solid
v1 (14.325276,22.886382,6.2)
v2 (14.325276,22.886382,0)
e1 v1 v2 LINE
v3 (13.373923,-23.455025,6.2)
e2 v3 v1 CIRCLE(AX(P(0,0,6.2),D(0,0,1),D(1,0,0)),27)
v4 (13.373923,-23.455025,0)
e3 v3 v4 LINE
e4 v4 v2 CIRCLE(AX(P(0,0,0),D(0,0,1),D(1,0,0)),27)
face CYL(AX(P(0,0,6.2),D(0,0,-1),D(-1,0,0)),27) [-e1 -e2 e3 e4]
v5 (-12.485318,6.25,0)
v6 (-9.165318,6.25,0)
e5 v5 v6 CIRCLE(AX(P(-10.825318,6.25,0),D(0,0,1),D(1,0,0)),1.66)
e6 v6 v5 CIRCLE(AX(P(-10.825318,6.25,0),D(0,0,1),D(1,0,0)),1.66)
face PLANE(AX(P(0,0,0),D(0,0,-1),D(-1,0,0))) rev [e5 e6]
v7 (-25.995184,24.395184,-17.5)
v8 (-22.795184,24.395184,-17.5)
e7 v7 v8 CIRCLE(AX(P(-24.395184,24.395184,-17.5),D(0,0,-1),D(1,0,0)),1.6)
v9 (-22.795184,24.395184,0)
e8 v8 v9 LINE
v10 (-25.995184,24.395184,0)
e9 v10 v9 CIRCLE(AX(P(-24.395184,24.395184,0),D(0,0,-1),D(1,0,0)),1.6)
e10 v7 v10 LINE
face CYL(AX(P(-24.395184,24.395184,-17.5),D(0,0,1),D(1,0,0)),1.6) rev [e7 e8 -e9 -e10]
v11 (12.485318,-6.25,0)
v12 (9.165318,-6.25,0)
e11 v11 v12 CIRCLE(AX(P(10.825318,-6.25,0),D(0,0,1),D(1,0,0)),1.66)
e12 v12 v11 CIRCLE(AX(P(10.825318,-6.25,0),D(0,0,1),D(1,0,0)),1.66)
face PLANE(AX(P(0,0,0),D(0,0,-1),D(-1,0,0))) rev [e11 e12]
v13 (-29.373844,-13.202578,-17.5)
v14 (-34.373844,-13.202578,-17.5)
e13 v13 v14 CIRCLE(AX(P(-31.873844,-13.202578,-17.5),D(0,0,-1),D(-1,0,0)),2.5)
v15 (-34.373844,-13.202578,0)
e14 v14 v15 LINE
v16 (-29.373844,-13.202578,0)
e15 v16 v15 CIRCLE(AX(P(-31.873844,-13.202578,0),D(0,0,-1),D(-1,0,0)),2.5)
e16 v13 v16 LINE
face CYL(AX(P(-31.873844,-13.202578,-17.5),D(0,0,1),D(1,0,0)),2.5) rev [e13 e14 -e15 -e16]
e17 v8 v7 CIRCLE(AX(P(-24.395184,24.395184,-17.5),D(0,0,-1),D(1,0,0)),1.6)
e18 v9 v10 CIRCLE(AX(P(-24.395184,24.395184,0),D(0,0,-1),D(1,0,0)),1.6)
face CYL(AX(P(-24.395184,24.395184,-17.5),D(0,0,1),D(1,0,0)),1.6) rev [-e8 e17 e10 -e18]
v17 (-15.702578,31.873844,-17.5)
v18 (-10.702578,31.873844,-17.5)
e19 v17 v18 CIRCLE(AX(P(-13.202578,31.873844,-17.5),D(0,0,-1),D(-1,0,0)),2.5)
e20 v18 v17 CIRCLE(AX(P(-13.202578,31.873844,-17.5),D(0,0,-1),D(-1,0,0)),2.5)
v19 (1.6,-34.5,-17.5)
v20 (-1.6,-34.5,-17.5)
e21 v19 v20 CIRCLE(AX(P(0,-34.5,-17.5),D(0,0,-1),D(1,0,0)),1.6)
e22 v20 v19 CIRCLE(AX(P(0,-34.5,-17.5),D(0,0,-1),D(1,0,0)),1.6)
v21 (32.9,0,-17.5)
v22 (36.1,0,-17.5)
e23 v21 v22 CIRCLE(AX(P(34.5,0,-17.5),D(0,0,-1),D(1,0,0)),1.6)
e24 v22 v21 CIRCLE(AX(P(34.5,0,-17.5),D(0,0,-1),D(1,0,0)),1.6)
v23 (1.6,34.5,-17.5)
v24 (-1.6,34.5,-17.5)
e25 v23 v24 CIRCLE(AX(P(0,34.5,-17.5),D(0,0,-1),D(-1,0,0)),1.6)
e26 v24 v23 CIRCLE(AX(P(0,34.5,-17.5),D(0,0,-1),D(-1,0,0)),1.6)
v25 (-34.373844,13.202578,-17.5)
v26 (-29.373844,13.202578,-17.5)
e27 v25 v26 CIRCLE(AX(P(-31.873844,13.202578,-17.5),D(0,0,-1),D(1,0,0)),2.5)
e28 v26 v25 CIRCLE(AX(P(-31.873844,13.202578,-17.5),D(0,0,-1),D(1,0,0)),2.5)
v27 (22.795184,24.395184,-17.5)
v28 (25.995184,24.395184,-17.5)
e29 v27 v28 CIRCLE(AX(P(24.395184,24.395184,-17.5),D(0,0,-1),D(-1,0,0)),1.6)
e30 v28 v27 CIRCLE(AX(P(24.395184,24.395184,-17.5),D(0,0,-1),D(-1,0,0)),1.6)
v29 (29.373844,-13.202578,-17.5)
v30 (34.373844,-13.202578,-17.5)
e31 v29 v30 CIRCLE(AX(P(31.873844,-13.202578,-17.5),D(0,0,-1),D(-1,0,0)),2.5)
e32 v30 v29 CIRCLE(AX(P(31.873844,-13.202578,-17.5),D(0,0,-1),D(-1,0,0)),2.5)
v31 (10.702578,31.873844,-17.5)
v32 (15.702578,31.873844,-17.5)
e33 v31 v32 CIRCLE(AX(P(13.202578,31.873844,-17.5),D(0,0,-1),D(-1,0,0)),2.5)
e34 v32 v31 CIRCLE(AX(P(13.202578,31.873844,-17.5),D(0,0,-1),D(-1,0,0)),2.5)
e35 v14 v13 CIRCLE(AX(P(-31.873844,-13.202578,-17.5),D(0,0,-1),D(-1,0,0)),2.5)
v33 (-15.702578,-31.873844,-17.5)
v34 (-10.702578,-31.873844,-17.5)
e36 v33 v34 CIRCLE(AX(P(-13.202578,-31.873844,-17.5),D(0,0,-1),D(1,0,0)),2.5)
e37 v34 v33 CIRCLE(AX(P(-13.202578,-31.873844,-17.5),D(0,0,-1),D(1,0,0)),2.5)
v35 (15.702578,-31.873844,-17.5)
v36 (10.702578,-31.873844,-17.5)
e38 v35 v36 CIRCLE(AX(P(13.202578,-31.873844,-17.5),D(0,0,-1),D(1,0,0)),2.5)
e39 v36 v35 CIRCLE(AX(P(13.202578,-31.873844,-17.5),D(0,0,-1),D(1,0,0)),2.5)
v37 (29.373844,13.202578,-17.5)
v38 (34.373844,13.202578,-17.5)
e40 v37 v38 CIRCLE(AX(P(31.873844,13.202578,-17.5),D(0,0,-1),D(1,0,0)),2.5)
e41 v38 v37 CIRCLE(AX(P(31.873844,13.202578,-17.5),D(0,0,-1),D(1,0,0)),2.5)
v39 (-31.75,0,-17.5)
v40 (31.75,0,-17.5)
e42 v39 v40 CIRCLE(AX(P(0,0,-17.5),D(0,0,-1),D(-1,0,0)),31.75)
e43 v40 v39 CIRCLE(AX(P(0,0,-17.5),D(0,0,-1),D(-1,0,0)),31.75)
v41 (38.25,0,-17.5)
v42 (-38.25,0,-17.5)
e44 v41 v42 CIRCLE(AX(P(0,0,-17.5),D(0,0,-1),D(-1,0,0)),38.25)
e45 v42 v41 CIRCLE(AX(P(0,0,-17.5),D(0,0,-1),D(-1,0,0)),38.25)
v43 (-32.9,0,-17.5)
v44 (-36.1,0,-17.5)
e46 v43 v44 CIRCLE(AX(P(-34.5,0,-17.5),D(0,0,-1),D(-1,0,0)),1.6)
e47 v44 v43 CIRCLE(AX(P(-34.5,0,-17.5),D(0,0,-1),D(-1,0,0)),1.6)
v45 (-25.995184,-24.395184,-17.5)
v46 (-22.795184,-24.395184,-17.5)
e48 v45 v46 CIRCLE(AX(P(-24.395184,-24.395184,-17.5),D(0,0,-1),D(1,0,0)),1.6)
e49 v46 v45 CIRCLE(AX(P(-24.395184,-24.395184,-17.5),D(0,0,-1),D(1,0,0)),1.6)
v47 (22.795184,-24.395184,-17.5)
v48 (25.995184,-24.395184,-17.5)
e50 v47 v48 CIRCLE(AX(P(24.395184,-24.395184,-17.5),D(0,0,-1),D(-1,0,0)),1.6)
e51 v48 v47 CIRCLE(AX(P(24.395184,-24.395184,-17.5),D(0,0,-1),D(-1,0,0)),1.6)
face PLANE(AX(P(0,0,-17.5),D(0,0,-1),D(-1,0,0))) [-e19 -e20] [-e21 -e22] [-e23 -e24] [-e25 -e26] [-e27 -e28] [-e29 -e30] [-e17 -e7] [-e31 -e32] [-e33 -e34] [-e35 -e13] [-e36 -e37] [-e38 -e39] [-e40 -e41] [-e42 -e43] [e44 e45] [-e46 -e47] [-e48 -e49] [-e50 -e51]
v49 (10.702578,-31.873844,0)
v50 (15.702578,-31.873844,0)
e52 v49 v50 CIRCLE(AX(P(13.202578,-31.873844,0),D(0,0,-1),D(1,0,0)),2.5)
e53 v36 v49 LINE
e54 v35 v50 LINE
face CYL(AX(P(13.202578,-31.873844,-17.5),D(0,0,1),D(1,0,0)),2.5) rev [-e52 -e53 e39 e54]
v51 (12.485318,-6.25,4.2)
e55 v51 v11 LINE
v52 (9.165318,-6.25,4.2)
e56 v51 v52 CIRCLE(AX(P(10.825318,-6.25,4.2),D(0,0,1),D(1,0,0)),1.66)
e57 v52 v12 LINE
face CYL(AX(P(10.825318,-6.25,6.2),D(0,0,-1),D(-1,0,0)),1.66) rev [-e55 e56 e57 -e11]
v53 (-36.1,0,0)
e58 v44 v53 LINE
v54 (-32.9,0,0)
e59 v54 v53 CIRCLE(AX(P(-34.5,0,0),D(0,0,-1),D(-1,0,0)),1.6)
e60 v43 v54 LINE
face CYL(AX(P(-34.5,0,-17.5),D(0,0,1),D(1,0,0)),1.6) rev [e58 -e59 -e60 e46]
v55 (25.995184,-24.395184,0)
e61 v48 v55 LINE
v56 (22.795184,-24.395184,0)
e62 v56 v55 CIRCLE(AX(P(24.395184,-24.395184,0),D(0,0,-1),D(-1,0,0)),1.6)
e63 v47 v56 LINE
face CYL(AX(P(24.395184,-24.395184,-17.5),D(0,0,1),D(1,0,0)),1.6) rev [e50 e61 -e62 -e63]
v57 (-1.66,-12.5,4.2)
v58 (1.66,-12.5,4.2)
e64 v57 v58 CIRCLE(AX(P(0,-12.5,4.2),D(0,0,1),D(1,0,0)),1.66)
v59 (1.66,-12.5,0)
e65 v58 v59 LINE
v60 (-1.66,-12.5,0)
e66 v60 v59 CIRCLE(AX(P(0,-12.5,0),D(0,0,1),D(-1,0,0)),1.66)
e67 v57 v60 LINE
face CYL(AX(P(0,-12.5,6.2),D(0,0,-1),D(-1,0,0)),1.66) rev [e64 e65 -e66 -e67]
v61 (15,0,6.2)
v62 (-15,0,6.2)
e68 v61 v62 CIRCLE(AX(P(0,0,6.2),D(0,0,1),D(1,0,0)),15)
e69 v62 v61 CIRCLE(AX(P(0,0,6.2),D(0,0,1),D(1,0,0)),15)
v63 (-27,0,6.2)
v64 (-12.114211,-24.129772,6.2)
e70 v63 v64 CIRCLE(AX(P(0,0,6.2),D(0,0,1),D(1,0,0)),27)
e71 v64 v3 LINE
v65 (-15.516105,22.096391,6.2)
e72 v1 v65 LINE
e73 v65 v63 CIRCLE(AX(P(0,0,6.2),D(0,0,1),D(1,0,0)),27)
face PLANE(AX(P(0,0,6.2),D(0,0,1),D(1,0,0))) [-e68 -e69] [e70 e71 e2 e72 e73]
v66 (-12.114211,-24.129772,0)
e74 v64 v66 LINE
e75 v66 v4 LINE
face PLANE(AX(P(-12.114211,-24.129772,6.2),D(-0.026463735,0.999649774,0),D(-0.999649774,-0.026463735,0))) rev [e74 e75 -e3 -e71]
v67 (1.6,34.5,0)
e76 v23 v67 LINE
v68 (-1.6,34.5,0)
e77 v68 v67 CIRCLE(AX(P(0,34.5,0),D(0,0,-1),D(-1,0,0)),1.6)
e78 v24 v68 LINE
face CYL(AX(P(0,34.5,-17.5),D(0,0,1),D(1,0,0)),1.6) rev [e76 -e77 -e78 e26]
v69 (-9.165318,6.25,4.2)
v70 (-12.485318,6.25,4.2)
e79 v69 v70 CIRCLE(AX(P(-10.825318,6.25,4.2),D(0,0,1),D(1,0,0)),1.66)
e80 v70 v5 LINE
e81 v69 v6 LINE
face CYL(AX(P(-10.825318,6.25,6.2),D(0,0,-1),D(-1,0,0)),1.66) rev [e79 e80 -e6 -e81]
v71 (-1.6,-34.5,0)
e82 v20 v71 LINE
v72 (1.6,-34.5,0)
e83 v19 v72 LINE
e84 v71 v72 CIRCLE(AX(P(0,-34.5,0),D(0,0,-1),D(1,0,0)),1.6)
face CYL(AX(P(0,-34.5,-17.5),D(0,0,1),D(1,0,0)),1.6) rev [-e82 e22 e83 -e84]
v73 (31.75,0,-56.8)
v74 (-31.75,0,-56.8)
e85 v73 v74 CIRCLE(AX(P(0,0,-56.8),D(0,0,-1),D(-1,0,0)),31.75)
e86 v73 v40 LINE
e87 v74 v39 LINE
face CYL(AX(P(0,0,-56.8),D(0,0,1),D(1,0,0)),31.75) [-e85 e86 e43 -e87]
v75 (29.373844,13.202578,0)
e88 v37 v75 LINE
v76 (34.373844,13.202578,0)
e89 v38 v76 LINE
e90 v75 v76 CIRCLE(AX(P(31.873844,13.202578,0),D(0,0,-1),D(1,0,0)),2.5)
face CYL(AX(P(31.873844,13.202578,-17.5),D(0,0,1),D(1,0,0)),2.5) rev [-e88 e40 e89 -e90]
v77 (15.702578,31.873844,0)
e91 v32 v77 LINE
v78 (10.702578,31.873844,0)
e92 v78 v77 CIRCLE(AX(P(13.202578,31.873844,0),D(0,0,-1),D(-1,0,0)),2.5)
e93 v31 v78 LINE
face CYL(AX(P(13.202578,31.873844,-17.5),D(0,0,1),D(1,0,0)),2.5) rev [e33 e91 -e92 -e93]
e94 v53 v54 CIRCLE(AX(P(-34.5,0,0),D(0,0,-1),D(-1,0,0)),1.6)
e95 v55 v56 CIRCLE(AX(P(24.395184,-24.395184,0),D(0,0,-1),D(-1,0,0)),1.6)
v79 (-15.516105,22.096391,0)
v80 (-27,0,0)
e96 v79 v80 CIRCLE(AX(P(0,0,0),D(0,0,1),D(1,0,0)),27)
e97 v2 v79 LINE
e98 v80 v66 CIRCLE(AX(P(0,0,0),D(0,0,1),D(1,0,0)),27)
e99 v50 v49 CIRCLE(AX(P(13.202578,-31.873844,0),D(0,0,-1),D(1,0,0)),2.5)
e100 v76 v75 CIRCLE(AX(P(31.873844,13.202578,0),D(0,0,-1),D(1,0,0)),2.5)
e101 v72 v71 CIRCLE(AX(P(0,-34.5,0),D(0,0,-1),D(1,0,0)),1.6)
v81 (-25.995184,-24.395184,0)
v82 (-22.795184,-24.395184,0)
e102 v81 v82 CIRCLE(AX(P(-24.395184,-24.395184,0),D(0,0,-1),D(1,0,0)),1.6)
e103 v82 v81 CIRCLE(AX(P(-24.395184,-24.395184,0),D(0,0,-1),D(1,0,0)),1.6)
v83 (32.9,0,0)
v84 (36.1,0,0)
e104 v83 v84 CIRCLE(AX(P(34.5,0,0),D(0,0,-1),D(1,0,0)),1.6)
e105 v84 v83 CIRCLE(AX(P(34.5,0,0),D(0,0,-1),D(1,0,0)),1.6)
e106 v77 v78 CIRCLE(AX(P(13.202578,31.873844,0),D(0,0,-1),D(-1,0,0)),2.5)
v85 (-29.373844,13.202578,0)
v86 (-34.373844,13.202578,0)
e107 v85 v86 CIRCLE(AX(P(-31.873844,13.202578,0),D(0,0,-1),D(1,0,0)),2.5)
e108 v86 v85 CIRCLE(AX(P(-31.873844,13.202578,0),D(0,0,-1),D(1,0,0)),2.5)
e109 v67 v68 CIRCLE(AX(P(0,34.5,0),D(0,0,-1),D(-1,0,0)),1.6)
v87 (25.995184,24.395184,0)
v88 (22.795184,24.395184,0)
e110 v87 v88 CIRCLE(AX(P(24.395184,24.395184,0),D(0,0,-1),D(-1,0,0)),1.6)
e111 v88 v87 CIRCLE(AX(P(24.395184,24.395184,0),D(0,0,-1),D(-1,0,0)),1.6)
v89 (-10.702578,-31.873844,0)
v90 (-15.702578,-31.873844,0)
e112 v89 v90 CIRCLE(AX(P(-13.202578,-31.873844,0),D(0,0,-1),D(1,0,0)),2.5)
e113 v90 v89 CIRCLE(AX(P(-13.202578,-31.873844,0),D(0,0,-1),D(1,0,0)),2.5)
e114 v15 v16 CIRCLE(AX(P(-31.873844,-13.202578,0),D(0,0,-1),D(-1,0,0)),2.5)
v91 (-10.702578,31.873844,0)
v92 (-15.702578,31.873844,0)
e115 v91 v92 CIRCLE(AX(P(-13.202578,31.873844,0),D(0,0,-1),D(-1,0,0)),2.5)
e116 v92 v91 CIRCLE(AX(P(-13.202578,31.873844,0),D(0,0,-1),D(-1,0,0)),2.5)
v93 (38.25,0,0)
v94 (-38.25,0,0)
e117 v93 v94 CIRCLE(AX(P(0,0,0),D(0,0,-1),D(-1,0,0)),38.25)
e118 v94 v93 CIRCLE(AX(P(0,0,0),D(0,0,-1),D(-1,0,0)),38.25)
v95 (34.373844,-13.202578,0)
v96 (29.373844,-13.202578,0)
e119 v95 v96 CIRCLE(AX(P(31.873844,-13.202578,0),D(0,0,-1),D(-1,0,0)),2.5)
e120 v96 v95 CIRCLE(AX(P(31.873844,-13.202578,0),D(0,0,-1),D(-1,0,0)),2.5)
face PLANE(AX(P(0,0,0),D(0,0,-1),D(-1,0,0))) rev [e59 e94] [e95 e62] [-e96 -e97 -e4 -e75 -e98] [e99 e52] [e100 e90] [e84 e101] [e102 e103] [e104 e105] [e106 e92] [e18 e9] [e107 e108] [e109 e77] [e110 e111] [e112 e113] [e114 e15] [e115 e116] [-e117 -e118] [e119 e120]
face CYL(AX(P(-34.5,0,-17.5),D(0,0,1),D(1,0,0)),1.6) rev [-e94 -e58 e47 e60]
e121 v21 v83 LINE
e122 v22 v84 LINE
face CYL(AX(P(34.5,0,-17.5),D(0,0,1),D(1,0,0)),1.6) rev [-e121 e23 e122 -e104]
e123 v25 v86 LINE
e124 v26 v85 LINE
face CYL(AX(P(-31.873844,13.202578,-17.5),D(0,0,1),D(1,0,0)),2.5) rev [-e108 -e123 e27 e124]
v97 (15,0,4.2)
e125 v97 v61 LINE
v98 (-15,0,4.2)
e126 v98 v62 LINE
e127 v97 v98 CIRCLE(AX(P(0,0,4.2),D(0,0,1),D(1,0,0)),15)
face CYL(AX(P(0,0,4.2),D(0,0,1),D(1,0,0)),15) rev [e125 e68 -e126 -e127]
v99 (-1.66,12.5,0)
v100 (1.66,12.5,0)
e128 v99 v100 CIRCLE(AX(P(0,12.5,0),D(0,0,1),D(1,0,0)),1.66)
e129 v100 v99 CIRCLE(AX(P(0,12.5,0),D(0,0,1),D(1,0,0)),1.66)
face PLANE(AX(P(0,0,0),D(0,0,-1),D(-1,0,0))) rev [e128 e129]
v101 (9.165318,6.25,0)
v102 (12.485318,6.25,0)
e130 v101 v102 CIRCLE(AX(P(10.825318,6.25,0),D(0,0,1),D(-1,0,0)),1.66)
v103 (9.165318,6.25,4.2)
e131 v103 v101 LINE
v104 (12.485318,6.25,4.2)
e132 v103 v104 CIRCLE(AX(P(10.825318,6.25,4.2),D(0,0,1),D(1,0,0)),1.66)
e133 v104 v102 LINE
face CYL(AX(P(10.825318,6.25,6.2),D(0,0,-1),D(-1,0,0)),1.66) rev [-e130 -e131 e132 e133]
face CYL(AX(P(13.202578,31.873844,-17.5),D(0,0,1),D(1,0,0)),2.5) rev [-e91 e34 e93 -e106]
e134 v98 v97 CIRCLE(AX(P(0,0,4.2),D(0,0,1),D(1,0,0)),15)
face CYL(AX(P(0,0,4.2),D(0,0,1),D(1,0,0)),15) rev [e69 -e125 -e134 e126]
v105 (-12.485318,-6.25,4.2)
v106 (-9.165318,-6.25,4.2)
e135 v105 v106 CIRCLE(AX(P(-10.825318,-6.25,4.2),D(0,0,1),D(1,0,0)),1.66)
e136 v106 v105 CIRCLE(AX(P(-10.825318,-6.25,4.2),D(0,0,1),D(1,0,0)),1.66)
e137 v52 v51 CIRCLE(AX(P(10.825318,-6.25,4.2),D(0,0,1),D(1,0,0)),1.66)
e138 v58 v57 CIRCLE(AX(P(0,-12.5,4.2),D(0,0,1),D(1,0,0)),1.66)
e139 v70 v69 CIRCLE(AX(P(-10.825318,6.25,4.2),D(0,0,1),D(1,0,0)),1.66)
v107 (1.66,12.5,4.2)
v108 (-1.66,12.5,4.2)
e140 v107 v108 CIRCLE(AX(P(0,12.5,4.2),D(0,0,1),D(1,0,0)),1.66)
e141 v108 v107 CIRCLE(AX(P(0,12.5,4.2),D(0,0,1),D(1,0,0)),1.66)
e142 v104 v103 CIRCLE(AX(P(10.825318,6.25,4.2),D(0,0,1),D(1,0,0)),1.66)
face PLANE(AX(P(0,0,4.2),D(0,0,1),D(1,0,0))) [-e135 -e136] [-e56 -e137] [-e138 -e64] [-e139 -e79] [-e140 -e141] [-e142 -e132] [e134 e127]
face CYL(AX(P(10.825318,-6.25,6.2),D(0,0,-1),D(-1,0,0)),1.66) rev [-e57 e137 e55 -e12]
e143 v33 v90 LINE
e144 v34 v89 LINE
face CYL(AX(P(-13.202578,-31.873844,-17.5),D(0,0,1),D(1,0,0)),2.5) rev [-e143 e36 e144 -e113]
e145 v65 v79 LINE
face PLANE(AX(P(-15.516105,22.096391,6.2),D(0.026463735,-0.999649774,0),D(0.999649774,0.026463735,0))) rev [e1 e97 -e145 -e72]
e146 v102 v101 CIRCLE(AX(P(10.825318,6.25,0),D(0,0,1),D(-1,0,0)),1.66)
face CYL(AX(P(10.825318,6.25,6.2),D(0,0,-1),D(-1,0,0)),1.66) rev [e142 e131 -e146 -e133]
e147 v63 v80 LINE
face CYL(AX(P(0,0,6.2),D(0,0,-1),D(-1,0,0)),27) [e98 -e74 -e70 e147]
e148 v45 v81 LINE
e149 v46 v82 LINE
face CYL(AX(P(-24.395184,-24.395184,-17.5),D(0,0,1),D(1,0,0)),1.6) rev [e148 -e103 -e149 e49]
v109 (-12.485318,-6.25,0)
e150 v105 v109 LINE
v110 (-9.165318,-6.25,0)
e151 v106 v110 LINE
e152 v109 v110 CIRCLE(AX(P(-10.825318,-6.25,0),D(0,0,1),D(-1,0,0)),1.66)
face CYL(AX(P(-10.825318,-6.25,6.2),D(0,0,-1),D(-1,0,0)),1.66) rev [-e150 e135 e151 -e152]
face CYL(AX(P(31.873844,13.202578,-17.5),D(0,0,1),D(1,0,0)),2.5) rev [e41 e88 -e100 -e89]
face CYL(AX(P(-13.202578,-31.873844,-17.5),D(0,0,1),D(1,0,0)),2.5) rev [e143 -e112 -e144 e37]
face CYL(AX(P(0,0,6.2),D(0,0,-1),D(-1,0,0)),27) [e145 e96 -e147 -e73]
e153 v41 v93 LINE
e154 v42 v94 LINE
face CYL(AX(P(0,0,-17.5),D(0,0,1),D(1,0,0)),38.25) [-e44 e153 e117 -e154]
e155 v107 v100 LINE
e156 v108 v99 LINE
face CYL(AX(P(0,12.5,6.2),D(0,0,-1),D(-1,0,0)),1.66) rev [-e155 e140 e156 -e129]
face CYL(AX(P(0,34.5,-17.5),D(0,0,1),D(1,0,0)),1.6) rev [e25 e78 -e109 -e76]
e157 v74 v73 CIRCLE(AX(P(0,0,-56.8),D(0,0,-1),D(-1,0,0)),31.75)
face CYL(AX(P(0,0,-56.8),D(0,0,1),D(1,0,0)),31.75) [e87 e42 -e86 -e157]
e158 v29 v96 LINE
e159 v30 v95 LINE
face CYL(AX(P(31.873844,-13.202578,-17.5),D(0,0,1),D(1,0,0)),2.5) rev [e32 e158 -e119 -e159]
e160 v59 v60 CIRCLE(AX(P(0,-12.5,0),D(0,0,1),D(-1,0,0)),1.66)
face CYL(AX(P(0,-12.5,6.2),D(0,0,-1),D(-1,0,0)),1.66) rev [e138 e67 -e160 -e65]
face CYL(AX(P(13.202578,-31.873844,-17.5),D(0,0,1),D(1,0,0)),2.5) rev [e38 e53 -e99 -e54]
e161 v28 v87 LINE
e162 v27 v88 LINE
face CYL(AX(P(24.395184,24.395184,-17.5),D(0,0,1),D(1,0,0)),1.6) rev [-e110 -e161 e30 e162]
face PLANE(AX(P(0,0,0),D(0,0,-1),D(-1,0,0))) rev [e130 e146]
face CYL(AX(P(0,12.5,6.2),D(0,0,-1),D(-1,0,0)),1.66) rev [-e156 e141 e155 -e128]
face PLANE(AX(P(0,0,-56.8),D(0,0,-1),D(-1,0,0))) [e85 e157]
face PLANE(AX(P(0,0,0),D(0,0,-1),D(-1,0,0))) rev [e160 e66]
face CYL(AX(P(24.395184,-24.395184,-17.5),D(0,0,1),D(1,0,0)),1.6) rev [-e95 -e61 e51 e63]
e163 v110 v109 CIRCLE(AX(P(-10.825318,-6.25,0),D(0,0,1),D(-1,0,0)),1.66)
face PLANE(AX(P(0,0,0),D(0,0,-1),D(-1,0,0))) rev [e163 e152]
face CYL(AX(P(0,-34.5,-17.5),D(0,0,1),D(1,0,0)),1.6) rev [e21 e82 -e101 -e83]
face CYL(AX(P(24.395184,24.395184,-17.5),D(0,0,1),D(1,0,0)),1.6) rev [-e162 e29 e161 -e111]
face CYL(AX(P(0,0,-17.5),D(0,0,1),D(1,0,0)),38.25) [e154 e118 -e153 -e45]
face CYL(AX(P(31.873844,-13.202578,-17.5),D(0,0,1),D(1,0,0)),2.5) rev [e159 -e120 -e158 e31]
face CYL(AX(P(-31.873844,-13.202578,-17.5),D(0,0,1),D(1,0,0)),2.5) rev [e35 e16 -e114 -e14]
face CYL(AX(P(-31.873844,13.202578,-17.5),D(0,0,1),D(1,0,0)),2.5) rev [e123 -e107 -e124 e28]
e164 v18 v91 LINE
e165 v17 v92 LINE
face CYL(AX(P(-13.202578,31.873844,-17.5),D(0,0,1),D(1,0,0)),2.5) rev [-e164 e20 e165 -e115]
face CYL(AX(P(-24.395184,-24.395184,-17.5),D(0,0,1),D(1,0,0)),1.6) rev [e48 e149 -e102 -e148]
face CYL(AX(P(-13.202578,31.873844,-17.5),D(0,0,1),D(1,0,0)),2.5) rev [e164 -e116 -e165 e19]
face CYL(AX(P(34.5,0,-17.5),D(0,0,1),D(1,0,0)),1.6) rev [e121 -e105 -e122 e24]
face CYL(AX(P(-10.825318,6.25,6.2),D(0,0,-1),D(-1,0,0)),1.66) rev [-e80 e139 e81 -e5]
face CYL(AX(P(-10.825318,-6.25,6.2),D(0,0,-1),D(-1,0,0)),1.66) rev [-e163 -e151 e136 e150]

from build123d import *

# Parameters (mm, degrees)
SKETCH1_R           = 1.66
BOSS_EXTRUDE1_DEPTH = 6.2
SKETCH2_R           = 38.25
SKETCH2_R_2         = 1.6
SKETCH2_R_3         = 2.5
BOSS_EXTRUDE2_DEPTH = 17.5
SKETCH3_R           = 31.75
BOSS_EXTRUDE3_DEPTH = 39.3
SKETCH4_R           = 15
CUT_EXTRUDE1_DEPTH  = 2


with BuildPart() as part:
    # Sketch1 → Boss-Extrude1 (new body)
    with BuildSketch(Plane.XY):
        with BuildLine():
            Line((-15.516105129, 22.096390692), (14.325275898, 22.886381768))
            ThreePointArc((14.325275898, 22.886381768), (26.994312242, -0.554171996), (13.373923279, -23.455024539))
            Line((13.373923279, -23.455024539), (-12.114210645, -24.129772076))
            ThreePointArc((-12.114210645, -24.129772076), (-26.927181778, -1.981636062), (-15.516105129, 22.096390692))
        make_face()
        with Locations(Location((0, 12.5, 0), (0, 0, 180))):
            Circle(SKETCH1_R, mode=Mode.SUBTRACT)
        with Locations(Location((10.825317547, 6.25, 0), (0, 0, 180))):
            Circle(SKETCH1_R, mode=Mode.SUBTRACT)
        with Locations(Location((0, -12.5, 0), (0, 0, 180))):
            Circle(SKETCH1_R, mode=Mode.SUBTRACT)
        with Locations(Location((10.825317547, -6.25, 0), (0, 0, 180))):
            Circle(SKETCH1_R, mode=Mode.SUBTRACT)
        with Locations(Location((-10.825317547, -6.25, 0), (0, 0, 180))):
            Circle(SKETCH1_R, mode=Mode.SUBTRACT)
        with Locations(Location((-10.825317547, 6.25, 0), (0, 0, 180))):
            Circle(SKETCH1_R, mode=Mode.SUBTRACT)
    extrude(amount=BOSS_EXTRUDE1_DEPTH)

    # Sketch2 → Boss-Extrude2 (add)
    with BuildSketch(Plane(origin=(0, 0, 0), x_dir=(-1, 0, 0), z_dir=(0, 0, -1))):
        Circle(SKETCH2_R)
        with Locations((0, 34.5)):
            Circle(SKETCH2_R_2, mode=Mode.SUBTRACT)
        with Locations(Location((24.395183951, 24.395183951, 0), (0, 0, 180))):
            Circle(SKETCH2_R_2, mode=Mode.SUBTRACT)
        with Locations((34.5, 0)):
            Circle(SKETCH2_R_2, mode=Mode.SUBTRACT)
        with Locations(Location((24.395183951, -24.395183951, 0), (0, 0, 180))):
            Circle(SKETCH2_R_2, mode=Mode.SUBTRACT)
        with Locations(Location((0, -34.5, 0), (0, 0, 180))):
            Circle(SKETCH2_R_2, mode=Mode.SUBTRACT)
        with Locations((-24.395183951, -24.395183951)):
            Circle(SKETCH2_R_2, mode=Mode.SUBTRACT)
        with Locations(Location((-34.5, 0, 0), (0, 0, 180))):
            Circle(SKETCH2_R_2, mode=Mode.SUBTRACT)
        with Locations((-24.395183951, 24.395183951)):
            Circle(SKETCH2_R_2, mode=Mode.SUBTRACT)
        with Locations((13.202578417, 31.873843872)):
            Circle(SKETCH2_R_3, mode=Mode.SUBTRACT)
        with Locations(Location((31.873843872, 13.202578417, 0), (0, 0, 180))):
            Circle(SKETCH2_R_3, mode=Mode.SUBTRACT)
        with Locations((31.873843872, -13.202578417)):
            Circle(SKETCH2_R_3, mode=Mode.SUBTRACT)
        with Locations(Location((13.202578417, -31.873843872, 0), (0, 0, 180))):
            Circle(SKETCH2_R_3, mode=Mode.SUBTRACT)
        with Locations((-31.873843872, -13.202578417)):
            Circle(SKETCH2_R_3, mode=Mode.SUBTRACT)
        with Locations(Location((-31.873843872, 13.202578417, 0), (0, 0, 180))):
            Circle(SKETCH2_R_3, mode=Mode.SUBTRACT)
        with Locations((-13.202578417, 31.873843872)):
            Circle(SKETCH2_R_3, mode=Mode.SUBTRACT)
        with Locations(Location((-13.202578417, -31.873843872, 0), (0, 0, 180))):
            Circle(SKETCH2_R_3, mode=Mode.SUBTRACT)
    extrude(amount=BOSS_EXTRUDE2_DEPTH)

    # Sketch3 → Boss-Extrude3 (add)
    with BuildSketch(Plane(origin=(0, 0, -17.5), x_dir=(-1, 0, 0), z_dir=(0, 0, -1))):
        Circle(SKETCH3_R)
    extrude(amount=BOSS_EXTRUDE3_DEPTH)

    # Sketch4 → Cut-Extrude1 (cut)
    with BuildSketch(Plane.XY.offset(6.2)):
        Circle(SKETCH4_R)
    extrude(amount=-CUT_EXTRUDE1_DEPTH, mode=Mode.SUBTRACT)


solid = part.part
